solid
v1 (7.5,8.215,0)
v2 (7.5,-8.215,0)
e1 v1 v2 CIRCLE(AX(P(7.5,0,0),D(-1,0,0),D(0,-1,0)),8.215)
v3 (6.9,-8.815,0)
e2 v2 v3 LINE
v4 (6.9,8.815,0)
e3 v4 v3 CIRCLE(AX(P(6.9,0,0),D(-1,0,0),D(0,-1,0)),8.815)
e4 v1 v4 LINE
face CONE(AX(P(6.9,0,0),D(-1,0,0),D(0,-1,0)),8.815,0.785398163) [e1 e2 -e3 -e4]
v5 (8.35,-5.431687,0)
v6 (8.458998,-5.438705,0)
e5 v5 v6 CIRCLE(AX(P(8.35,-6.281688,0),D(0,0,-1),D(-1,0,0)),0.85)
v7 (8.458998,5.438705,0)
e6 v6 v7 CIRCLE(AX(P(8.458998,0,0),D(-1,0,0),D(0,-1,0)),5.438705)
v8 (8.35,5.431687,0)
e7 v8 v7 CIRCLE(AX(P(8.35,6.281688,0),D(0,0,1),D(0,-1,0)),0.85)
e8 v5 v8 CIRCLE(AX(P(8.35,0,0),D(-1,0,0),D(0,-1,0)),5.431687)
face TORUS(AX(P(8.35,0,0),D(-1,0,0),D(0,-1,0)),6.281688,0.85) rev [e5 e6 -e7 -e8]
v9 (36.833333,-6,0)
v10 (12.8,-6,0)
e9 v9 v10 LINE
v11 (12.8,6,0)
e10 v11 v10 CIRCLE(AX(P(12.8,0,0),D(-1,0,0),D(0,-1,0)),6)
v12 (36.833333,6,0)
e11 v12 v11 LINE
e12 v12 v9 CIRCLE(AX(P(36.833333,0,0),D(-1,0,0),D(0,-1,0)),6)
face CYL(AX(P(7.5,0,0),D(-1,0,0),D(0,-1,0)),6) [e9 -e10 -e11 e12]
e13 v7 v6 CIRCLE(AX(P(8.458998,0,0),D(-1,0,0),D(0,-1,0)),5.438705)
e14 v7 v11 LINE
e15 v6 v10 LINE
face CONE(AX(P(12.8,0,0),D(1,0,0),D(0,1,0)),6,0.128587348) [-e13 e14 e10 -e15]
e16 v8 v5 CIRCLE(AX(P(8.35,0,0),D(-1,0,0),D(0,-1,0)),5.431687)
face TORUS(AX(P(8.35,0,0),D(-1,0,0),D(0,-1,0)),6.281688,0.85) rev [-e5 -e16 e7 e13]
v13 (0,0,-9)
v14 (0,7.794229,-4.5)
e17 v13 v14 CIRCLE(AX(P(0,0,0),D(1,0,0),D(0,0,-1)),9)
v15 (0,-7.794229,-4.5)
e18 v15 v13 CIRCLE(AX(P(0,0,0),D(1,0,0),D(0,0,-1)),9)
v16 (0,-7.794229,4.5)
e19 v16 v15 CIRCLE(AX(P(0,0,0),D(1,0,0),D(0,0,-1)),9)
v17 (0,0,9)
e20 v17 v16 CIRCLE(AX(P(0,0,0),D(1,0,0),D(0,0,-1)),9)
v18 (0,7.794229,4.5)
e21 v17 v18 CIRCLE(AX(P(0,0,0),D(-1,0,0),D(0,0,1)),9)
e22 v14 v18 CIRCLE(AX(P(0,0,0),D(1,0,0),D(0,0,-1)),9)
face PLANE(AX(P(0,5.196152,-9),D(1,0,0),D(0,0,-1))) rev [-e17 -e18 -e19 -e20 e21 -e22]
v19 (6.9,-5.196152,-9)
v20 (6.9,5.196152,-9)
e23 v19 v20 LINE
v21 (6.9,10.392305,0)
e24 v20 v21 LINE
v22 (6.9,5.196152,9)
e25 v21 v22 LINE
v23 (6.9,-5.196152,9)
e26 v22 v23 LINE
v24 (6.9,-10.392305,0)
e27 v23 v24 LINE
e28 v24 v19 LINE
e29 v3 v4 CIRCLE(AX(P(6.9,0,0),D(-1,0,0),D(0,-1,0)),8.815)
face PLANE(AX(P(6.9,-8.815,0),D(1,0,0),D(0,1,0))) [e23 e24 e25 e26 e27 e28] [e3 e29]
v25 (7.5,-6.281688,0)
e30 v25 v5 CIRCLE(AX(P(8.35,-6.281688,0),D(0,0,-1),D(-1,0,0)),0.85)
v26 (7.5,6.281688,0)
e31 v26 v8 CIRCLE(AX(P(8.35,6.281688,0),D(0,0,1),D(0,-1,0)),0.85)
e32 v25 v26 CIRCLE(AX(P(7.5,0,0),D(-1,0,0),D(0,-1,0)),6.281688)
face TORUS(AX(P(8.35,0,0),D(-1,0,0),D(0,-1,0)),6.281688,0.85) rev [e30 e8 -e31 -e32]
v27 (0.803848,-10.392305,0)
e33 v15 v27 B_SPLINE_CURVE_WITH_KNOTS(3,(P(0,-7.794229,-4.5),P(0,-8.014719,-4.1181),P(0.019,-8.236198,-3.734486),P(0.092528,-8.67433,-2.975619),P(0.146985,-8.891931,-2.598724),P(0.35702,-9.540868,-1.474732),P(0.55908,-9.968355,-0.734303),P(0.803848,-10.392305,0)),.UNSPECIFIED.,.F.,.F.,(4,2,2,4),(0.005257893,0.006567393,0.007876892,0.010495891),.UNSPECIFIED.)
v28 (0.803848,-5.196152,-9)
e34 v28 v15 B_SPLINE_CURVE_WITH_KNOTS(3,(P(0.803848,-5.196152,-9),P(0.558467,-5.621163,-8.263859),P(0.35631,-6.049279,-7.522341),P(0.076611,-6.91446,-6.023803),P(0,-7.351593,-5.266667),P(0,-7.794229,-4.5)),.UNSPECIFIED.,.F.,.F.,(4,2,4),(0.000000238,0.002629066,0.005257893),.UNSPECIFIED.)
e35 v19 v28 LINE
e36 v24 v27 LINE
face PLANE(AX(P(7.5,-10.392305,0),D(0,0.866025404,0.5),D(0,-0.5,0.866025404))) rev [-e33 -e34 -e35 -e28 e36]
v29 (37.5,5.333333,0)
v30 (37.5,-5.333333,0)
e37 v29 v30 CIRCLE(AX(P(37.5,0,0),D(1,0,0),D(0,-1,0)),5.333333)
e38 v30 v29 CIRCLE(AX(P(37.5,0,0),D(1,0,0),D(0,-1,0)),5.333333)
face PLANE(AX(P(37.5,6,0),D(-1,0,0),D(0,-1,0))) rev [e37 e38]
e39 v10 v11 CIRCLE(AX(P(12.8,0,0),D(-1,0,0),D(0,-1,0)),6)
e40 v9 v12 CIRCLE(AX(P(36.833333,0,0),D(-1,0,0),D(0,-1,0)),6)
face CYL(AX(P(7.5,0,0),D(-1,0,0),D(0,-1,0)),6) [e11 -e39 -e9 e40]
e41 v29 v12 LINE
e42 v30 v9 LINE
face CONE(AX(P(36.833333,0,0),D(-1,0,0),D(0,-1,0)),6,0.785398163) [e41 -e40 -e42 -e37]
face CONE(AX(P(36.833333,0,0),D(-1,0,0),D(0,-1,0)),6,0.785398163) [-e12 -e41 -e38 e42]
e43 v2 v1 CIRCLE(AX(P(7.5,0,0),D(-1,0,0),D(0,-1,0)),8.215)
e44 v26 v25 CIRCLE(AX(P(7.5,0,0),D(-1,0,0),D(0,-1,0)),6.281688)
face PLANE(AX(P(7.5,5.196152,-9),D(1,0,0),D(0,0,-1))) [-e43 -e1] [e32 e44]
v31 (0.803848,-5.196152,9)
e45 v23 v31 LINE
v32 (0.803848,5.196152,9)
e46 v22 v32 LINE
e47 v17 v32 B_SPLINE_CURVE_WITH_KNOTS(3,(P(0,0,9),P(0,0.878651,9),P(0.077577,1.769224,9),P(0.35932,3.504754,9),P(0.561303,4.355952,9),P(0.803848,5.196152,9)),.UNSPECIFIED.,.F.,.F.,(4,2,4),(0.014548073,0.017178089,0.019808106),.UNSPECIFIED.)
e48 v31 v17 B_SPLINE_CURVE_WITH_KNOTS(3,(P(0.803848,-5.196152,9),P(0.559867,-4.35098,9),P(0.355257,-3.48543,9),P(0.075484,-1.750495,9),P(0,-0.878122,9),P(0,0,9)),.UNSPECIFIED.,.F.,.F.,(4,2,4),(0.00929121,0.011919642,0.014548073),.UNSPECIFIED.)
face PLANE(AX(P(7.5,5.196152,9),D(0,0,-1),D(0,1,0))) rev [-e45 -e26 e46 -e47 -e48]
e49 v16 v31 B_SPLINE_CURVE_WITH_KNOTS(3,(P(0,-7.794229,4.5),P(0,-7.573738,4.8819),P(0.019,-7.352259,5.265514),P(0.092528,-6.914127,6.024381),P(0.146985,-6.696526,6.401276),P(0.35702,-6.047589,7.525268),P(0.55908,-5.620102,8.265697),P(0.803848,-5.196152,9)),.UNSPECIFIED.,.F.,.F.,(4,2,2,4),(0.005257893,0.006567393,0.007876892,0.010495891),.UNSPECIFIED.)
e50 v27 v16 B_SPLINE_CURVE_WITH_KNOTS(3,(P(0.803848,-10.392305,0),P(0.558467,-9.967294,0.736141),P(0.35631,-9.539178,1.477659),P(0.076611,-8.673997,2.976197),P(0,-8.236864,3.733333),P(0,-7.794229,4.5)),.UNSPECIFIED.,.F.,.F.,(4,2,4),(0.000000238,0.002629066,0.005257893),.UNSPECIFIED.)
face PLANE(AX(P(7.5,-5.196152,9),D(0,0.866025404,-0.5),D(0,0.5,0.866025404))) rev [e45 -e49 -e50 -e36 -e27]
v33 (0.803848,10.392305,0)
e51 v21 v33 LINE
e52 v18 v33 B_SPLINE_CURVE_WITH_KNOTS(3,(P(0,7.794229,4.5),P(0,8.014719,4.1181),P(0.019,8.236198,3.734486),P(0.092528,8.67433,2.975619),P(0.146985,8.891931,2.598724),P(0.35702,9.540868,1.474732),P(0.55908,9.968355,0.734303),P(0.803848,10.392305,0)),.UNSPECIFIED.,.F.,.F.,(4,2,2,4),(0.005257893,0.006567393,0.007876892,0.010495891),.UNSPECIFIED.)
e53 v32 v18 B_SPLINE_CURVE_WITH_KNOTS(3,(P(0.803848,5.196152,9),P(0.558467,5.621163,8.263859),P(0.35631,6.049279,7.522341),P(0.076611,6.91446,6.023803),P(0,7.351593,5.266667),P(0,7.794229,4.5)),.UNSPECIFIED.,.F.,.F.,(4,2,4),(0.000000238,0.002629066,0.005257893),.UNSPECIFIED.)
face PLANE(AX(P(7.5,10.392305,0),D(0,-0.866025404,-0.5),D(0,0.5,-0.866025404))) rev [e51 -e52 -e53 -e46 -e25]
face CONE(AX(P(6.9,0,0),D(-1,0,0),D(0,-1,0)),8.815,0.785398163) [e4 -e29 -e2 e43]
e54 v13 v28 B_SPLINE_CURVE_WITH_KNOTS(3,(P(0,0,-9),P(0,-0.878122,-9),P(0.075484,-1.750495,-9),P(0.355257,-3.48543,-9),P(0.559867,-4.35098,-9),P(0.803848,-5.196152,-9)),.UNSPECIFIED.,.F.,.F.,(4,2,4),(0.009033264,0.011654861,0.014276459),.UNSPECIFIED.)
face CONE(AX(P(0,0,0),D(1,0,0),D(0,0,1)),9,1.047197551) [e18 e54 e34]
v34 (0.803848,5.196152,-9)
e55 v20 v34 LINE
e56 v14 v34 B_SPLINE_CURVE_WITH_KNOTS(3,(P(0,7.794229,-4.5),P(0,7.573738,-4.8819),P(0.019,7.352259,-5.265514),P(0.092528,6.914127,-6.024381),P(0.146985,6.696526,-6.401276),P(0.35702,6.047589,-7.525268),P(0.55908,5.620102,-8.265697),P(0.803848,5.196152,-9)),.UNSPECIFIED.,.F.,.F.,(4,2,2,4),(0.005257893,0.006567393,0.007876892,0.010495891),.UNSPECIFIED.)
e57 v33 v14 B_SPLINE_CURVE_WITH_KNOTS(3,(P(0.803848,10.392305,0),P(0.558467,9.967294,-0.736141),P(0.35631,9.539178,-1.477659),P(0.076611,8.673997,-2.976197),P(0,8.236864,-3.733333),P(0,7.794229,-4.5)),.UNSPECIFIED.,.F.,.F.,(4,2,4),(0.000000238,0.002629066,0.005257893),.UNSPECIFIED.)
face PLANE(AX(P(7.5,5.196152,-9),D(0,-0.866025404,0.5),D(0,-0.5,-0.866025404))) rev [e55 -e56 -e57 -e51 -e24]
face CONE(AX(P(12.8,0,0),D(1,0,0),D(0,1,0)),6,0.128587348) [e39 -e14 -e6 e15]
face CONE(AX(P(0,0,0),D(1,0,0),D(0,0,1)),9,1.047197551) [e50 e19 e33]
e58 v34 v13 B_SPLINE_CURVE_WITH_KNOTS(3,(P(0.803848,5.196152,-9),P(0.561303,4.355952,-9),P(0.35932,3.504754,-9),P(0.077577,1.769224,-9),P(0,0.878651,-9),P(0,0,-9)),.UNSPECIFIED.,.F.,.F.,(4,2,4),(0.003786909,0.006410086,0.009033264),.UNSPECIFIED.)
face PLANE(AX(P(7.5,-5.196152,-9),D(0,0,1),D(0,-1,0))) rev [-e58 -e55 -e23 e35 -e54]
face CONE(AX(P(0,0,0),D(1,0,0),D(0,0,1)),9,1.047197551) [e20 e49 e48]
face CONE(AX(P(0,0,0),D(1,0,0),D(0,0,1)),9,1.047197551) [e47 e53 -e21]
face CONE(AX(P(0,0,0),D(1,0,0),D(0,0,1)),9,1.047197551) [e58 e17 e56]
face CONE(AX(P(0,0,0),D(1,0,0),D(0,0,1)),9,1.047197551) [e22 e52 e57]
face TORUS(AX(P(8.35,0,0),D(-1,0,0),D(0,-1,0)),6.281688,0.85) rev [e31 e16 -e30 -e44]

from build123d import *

# Parameters (mm, degrees)
EXTRUDE_1_DEPTH     = 7.5
SKETCH_4_R          = 20.03
SKETCH_4_R_2        = 9
CUT_EXTRUDE_1_DEPTH = 0.9375
CUT_EXTRUDE_1_DRAFT = -60
CHAMFER_1_SIZE      = 0.666666667


with BuildPart() as part:
    # 草图3 → 凸台-拉伸1 (new body)
    with BuildSketch(Plane(origin=(0, 0, 0), x_dir=(0, 0, -1), z_dir=(1, 0, 0))):
        Polygon((9, 5.196152423), (0, 10.392304845), (-9, 5.196152423), (-9, -5.196152423), (0, -10.392304845), (9, -5.196152423), align=None)
    extrude(amount=EXTRUDE_1_DEPTH)


with BuildPart() as cut_extrude_1_tool:
    # 草图4 → 切除-拉伸1 (with draft: the straight prism first)
    with BuildSketch(Plane.ZY):
        Circle(SKETCH_4_R)
        Circle(SKETCH_4_R_2, mode=Mode.SUBTRACT)
    extrude(amount=-CUT_EXTRUDE_1_DEPTH)
    # 切除-拉伸1: the draft: its side faces are tilted about the plane it starts from
    cut_extrude_1_sides = [cut_extrude_1_tool.faces().sort_by_distance(p)[0] for p in [
        (0.46875, 0, -20.03),
        (0.46875, 0, -9),
    ]]
    draft(cut_extrude_1_sides, Plane.ZY, CUT_EXTRUDE_1_DRAFT)


with BuildPart() as part_1:
    add(part.part)

    # 切除-拉伸1: cut by cut_extrude_1_tool
    add(cut_extrude_1_tool.part, mode=Mode.SUBTRACT)

    # 草图6 → 旋转2 (revolve)
    with BuildSketch(Plane.XY, mode=Mode.PRIVATE) as revolve_2_sk:
        with BuildLine():
            Line((12.8, 6), (37.5, 6))
            Line((37.5, 6), (37.5, 0))
            Line((37.5, 0), (7.5, 0))
            Line((7.5, 0), (7.5, 6.2816875))
            ThreePointArc((7.5, 6.2816875), (7.788817563, 5.643272061), (8.458998289, 5.438705073))
            Line((8.458998289, 5.438705073), (12.8, 6))
        make_face()
    revolve(revolve_2_sk.sketch.rotate(Axis((7.5, 0, 0), (1, 0, 0)), 180), axis=Axis((7.5, 0, 0), (1, 0, 0)))

    # 倒角1
    chamfer_1_edges = [part_1.edges().sort_by_distance(p)[0] for p in [
        (37.5, 6, 0),
    ]]
    chamfer(chamfer_1_edges, length=CHAMFER_1_SIZE)

    # 草图8 → 切除-旋转2 (revolve, cut)
    with BuildSketch(Plane.XY, mode=Mode.PRIVATE) as cut_revolve_2_sk:
        Polygon((7.5, 8.215), (6.9, 8.815), (6.9, 20.03), (7.5, 20.03), align=None)
    revolve(cut_revolve_2_sk.sketch.rotate(Axis((0, 0, 0), (1, 0, 0)), 180), axis=Axis((0, 0, 0), (1, 0, 0)), mode=Mode.SUBTRACT)


solid = part_1.part
